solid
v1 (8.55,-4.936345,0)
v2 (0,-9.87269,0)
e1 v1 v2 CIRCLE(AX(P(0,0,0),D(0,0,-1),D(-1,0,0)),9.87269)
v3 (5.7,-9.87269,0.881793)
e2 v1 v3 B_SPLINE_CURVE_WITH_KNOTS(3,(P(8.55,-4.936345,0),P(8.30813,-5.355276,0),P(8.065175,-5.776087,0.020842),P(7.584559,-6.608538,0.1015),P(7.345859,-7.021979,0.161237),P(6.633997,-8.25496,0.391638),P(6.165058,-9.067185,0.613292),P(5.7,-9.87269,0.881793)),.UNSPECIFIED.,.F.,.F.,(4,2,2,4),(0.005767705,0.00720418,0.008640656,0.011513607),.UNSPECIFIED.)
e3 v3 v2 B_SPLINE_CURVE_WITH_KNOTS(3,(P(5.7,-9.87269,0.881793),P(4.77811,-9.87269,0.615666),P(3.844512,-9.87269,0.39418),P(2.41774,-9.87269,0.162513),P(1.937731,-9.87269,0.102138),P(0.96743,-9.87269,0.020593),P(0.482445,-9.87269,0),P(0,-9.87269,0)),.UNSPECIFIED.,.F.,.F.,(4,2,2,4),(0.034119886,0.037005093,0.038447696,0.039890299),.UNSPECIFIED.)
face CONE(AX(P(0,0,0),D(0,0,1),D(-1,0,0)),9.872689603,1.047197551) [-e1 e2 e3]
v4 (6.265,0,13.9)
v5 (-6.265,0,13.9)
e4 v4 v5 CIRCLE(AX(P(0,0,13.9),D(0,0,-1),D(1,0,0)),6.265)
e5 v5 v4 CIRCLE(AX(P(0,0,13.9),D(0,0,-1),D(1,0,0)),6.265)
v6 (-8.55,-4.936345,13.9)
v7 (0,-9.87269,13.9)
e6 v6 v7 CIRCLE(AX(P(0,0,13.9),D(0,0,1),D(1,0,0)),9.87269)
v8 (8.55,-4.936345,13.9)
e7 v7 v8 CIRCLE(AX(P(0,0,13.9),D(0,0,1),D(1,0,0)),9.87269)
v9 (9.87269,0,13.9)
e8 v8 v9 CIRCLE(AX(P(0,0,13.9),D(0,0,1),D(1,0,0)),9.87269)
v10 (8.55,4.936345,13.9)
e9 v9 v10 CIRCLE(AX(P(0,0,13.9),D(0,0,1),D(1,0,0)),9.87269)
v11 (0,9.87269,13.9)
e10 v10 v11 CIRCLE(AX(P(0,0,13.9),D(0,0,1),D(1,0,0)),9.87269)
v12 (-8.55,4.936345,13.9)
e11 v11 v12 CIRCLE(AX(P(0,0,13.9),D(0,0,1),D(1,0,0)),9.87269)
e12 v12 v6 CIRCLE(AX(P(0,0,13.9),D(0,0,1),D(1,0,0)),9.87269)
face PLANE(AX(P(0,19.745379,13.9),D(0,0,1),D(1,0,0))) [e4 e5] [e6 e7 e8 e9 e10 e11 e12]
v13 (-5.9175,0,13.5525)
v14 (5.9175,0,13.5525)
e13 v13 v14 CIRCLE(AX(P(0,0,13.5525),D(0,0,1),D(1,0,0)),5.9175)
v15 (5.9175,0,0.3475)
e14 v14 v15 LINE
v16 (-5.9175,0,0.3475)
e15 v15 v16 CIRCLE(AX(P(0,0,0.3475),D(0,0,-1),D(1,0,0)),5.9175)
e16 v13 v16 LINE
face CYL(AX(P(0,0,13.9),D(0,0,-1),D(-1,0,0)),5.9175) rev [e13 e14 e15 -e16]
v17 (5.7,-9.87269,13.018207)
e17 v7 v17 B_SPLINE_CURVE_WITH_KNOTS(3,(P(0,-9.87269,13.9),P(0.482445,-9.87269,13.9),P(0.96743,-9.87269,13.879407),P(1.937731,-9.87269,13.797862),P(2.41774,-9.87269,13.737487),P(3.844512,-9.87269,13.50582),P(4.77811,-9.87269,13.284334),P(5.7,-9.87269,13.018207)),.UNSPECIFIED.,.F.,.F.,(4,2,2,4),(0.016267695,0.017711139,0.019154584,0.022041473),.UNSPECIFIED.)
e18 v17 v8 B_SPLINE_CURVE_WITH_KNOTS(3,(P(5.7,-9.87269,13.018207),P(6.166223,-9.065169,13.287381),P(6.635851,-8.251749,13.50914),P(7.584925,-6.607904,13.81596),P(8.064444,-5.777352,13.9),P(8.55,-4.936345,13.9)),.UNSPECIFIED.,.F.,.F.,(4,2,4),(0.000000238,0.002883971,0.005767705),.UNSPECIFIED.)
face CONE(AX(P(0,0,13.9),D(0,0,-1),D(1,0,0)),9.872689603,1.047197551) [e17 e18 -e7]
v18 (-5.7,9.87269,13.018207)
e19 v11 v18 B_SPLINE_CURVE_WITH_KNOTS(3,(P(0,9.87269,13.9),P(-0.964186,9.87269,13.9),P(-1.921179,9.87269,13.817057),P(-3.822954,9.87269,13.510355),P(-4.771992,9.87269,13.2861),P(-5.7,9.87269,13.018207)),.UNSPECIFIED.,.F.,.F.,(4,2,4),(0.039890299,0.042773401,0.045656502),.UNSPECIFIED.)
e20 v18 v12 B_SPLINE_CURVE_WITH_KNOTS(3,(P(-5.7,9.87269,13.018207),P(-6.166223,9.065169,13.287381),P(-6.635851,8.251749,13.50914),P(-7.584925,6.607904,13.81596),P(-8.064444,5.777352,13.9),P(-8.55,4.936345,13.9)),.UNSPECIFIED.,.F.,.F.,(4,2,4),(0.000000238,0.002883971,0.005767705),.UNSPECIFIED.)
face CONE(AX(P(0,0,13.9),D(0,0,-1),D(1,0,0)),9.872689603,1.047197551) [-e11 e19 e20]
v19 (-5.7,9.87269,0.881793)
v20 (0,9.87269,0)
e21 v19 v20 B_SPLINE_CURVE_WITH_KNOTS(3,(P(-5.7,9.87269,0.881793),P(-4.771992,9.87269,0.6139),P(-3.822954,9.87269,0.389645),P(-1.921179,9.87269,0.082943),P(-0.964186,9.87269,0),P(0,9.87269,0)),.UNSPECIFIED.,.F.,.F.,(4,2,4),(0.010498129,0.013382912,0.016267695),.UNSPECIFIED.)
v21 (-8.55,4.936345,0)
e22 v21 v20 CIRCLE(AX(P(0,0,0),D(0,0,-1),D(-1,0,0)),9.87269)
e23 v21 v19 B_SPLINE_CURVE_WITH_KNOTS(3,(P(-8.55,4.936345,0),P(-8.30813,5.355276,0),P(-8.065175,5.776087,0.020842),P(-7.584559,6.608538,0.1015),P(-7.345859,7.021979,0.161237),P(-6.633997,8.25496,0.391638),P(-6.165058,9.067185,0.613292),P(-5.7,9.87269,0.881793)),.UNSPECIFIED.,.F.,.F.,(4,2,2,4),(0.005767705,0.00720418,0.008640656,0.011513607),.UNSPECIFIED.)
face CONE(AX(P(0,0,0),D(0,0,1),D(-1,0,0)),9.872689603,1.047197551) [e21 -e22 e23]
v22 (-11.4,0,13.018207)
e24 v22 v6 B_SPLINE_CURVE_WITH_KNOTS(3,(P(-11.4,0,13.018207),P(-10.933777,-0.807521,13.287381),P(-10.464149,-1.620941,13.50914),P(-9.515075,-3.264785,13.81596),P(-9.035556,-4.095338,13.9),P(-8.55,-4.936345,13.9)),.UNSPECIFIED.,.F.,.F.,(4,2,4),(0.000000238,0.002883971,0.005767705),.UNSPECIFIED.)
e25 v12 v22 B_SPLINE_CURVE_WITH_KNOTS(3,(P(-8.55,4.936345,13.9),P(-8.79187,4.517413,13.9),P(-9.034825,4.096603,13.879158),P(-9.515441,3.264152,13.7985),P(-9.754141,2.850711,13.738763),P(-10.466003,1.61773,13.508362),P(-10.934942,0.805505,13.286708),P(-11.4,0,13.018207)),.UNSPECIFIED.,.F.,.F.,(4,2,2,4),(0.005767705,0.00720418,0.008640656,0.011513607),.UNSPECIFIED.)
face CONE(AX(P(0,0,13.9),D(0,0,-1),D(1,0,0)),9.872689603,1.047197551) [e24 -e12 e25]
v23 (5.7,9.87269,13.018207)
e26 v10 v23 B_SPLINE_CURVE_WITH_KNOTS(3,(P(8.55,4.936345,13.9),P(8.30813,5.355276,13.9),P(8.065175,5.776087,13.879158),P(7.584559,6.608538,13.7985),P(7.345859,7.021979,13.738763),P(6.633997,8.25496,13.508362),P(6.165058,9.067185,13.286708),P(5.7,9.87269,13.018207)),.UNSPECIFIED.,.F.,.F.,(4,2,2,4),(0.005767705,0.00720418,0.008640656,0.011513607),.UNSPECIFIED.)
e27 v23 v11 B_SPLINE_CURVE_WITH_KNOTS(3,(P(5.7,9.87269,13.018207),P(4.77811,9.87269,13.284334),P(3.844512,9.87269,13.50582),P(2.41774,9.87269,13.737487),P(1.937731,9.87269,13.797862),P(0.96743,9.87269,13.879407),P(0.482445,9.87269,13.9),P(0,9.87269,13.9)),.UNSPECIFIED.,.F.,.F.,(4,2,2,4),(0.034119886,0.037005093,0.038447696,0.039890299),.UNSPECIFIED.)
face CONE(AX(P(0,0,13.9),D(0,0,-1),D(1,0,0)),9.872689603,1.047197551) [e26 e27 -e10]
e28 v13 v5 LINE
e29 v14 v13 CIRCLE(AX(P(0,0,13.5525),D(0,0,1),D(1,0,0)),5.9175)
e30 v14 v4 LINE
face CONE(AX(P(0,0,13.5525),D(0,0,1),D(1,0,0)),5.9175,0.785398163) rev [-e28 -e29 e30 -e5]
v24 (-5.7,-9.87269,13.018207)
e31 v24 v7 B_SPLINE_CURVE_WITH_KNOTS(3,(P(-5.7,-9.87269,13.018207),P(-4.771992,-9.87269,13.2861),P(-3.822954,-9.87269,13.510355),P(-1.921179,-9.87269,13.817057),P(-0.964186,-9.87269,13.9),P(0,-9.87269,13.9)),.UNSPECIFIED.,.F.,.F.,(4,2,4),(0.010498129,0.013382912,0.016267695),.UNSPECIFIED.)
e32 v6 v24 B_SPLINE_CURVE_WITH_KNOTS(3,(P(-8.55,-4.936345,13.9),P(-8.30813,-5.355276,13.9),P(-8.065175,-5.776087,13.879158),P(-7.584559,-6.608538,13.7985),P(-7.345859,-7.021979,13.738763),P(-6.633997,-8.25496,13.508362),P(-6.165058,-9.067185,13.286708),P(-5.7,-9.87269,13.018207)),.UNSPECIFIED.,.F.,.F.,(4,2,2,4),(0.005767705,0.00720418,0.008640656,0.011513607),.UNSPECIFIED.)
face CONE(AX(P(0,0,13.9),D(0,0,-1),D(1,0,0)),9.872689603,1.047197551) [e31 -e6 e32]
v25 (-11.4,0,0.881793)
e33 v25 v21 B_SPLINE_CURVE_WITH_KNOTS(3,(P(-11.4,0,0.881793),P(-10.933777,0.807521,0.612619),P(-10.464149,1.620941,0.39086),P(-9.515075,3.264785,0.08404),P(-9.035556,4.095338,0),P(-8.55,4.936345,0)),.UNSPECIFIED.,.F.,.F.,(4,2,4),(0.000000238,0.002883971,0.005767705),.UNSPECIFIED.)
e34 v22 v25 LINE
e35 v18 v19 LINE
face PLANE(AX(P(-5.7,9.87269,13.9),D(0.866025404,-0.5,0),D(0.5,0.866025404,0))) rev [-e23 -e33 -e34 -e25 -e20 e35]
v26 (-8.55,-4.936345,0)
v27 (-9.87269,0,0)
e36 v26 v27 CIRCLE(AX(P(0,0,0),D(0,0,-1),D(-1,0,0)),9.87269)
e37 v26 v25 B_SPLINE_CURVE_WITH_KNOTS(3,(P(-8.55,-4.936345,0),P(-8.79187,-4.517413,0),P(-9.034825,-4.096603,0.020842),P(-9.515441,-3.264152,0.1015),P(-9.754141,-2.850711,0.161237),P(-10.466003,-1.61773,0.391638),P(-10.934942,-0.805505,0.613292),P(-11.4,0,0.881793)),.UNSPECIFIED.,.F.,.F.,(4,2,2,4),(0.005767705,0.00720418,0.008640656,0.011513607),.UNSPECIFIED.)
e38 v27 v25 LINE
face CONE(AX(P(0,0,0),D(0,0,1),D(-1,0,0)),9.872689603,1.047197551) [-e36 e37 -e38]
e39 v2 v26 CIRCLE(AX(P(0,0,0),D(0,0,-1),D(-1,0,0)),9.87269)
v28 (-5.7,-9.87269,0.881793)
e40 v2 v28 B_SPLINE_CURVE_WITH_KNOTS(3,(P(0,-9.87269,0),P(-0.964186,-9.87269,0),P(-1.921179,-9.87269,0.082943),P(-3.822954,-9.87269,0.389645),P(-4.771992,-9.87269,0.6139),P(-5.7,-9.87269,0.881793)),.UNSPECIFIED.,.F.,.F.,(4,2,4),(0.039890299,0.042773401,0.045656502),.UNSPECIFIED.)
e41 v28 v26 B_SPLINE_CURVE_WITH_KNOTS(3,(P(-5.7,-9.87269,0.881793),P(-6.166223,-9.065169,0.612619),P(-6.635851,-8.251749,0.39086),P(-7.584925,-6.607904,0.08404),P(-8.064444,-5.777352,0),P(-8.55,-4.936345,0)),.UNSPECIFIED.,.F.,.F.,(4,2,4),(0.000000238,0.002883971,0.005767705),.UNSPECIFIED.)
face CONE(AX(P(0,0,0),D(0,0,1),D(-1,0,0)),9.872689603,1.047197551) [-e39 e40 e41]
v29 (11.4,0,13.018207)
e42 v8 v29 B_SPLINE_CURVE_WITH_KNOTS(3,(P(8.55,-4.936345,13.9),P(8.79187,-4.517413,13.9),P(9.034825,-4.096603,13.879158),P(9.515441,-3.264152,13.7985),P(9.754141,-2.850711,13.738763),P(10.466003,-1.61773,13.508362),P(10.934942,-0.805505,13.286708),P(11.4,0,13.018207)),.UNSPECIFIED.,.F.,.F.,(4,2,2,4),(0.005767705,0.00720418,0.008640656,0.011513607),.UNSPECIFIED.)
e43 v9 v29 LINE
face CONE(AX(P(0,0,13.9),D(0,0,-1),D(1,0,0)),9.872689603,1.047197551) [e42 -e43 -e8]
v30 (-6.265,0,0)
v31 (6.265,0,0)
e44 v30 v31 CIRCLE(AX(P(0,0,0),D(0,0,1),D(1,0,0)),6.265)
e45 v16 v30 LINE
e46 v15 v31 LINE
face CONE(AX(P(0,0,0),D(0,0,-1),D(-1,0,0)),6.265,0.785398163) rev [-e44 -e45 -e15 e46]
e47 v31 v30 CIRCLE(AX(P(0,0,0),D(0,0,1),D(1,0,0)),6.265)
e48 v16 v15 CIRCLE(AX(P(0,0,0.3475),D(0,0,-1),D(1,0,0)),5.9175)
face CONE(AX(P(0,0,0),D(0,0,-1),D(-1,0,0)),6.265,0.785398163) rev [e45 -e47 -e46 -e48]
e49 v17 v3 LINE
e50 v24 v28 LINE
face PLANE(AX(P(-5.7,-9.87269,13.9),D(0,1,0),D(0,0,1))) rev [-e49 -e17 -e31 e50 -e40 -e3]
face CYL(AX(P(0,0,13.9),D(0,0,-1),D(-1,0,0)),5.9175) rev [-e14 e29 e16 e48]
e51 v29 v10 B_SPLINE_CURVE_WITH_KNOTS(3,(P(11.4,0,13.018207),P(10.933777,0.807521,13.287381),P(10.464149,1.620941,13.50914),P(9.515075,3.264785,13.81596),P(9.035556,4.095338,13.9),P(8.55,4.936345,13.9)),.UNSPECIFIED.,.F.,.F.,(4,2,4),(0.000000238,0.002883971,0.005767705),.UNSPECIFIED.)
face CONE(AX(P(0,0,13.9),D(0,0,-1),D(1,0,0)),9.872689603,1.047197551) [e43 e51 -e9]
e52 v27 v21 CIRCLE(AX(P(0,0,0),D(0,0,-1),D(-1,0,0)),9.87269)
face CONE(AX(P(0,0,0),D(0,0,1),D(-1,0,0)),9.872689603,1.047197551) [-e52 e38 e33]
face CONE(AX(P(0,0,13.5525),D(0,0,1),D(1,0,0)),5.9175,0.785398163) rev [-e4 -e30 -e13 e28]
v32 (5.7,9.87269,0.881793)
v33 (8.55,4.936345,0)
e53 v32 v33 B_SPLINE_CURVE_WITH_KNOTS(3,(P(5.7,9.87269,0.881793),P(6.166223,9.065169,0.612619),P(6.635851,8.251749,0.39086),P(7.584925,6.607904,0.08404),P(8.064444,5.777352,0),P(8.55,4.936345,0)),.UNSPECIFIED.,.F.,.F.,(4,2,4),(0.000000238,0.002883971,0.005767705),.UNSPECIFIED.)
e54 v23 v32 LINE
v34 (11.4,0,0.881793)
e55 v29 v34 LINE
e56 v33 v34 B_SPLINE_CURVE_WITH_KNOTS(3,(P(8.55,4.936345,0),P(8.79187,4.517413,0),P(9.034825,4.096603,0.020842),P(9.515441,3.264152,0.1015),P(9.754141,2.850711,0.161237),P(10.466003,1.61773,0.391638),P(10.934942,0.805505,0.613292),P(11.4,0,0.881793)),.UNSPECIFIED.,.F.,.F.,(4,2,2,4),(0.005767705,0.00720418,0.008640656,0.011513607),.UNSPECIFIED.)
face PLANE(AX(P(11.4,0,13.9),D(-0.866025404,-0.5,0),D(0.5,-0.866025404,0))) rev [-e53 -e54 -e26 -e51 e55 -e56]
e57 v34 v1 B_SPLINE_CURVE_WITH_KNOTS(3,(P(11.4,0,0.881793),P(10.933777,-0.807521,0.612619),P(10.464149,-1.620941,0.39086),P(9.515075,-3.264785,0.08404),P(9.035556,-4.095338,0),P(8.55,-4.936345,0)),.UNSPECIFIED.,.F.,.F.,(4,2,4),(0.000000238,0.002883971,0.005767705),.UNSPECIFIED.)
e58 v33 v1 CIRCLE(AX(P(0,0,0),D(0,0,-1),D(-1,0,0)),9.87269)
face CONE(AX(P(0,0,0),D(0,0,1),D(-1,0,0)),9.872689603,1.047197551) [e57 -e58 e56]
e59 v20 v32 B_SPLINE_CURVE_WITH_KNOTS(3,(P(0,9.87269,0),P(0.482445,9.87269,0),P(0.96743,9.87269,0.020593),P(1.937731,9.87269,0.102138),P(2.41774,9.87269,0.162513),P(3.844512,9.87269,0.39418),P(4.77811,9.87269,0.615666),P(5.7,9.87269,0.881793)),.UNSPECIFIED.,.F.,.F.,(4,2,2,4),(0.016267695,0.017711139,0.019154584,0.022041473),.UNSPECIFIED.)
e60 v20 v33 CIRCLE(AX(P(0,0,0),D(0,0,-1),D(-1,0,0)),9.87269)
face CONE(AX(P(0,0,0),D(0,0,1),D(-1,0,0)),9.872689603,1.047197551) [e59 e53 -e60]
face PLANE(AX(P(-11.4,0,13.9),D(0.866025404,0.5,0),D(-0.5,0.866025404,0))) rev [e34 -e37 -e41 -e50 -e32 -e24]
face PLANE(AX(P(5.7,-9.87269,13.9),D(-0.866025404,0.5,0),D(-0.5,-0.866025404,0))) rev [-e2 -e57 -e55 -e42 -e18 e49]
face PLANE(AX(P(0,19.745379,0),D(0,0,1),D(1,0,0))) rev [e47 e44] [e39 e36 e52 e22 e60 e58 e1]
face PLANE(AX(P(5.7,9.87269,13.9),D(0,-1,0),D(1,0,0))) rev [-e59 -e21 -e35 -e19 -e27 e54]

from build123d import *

# Parameters (mm, degrees)
SKETCH1_R          = 5.9175
BOSS_EXTRUDE_DEPTH = 13.9
SKETCH2_OUTSIDE_W  = 105.954
SKETCH2_OUTSIDE_H  = 102.9
SKETCH2_OUTSIDE_R  = 9.872689603
CUT_EXTRUDE1_DEPTH = 21.509509989
CUT_EXTRUDE1_DRAFT = -60
SKETCH3_OUTSIDE_W  = 105.954
SKETCH3_OUTSIDE_H  = 102.9
SKETCH3_OUTSIDE_R  = 9.872689603
CUT_EXTRUDE2_DEPTH = 21.509509989
CUT_EXTRUDE2_DRAFT = -60
CHAMFER1_SIZE      = 0.3475


with BuildPart() as part:
    # Sketch1 → Boss-Extrude (new body)
    with BuildSketch(Plane.XY):
        Polygon((5.7, 9.872689603), (-5.7, 9.872689603), (-11.4, 0), (-5.7, -9.872689603), (5.7, -9.872689603), (11.4, 0), align=None)
        Circle(SKETCH1_R, mode=Mode.SUBTRACT)
    extrude(amount=BOSS_EXTRUDE_DEPTH)


with BuildPart() as cut_extrude1_tool:
    # Sketch2 outside → Cut-Extrude1 (with draft: the straight prism first)
    with BuildSketch(Plane(origin=(0, 0, 0), x_dir=(-1, 0, 0), z_dir=(0, 0, -1))):
        Rectangle(SKETCH2_OUTSIDE_W, SKETCH2_OUTSIDE_H)
        Circle(SKETCH2_OUTSIDE_R, mode=Mode.SUBTRACT)
    extrude(amount=-CUT_EXTRUDE1_DEPTH)
    # Cut-Extrude1: the draft: its side faces are tilted about the plane it starts from
    cut_extrude1_sides = [cut_extrude1_tool.faces().sort_by_distance(p)[0] for p in [
        (0, -51.45, 10.754754995),
        (-52.977, 0, 10.754754995),
        (0, 51.45, 10.754754995),
        (52.977, 0, 10.754754995),
        (9.872689603, 0, 10.754754995),
    ]]
    draft(cut_extrude1_sides, Plane(origin=(0, 0, 0), x_dir=(-1, 0, 0), z_dir=(0, 0, -1)), CUT_EXTRUDE1_DRAFT)


with BuildPart() as part_1:
    add(part.part)

    # Cut-Extrude1: cut by cut_extrude1_tool
    add(cut_extrude1_tool.part, mode=Mode.SUBTRACT)


with BuildPart() as cut_extrude2_tool:
    # Sketch3 outside → Cut-Extrude2 (with draft: the straight prism first)
    with BuildSketch(Plane.XY.offset(13.9)):
        Rectangle(SKETCH3_OUTSIDE_W, SKETCH3_OUTSIDE_H)
        Circle(SKETCH3_OUTSIDE_R, mode=Mode.SUBTRACT)
    extrude(amount=-CUT_EXTRUDE2_DEPTH)
    # Cut-Extrude2: the draft: its side faces are tilted about the plane it starts from
    cut_extrude2_sides = [cut_extrude2_tool.faces().sort_by_distance(p)[0] for p in [
        (0, -51.45, 3.145245005),
        (52.977, 0, 3.145245005),
        (0, 51.45, 3.145245005),
        (-52.977, 0, 3.145245005),
        (-9.872689603, 0, 3.145245005),
    ]]
    draft(cut_extrude2_sides, Plane.XY.offset(13.9), CUT_EXTRUDE2_DRAFT)


with BuildPart() as part_2:
    add(part_1.part)

    # Cut-Extrude2: cut by cut_extrude2_tool
    add(cut_extrude2_tool.part, mode=Mode.SUBTRACT)

    # Chamfer1
    chamfer1_edges = [part_2.edges().sort_by_distance(p)[0] for p in [
        (-5.9175, 0, 0),
        (-5.9175, 0, 13.9),
    ]]
    chamfer(chamfer1_edges, length=CHAMFER1_SIZE)


solid = part_2.part
